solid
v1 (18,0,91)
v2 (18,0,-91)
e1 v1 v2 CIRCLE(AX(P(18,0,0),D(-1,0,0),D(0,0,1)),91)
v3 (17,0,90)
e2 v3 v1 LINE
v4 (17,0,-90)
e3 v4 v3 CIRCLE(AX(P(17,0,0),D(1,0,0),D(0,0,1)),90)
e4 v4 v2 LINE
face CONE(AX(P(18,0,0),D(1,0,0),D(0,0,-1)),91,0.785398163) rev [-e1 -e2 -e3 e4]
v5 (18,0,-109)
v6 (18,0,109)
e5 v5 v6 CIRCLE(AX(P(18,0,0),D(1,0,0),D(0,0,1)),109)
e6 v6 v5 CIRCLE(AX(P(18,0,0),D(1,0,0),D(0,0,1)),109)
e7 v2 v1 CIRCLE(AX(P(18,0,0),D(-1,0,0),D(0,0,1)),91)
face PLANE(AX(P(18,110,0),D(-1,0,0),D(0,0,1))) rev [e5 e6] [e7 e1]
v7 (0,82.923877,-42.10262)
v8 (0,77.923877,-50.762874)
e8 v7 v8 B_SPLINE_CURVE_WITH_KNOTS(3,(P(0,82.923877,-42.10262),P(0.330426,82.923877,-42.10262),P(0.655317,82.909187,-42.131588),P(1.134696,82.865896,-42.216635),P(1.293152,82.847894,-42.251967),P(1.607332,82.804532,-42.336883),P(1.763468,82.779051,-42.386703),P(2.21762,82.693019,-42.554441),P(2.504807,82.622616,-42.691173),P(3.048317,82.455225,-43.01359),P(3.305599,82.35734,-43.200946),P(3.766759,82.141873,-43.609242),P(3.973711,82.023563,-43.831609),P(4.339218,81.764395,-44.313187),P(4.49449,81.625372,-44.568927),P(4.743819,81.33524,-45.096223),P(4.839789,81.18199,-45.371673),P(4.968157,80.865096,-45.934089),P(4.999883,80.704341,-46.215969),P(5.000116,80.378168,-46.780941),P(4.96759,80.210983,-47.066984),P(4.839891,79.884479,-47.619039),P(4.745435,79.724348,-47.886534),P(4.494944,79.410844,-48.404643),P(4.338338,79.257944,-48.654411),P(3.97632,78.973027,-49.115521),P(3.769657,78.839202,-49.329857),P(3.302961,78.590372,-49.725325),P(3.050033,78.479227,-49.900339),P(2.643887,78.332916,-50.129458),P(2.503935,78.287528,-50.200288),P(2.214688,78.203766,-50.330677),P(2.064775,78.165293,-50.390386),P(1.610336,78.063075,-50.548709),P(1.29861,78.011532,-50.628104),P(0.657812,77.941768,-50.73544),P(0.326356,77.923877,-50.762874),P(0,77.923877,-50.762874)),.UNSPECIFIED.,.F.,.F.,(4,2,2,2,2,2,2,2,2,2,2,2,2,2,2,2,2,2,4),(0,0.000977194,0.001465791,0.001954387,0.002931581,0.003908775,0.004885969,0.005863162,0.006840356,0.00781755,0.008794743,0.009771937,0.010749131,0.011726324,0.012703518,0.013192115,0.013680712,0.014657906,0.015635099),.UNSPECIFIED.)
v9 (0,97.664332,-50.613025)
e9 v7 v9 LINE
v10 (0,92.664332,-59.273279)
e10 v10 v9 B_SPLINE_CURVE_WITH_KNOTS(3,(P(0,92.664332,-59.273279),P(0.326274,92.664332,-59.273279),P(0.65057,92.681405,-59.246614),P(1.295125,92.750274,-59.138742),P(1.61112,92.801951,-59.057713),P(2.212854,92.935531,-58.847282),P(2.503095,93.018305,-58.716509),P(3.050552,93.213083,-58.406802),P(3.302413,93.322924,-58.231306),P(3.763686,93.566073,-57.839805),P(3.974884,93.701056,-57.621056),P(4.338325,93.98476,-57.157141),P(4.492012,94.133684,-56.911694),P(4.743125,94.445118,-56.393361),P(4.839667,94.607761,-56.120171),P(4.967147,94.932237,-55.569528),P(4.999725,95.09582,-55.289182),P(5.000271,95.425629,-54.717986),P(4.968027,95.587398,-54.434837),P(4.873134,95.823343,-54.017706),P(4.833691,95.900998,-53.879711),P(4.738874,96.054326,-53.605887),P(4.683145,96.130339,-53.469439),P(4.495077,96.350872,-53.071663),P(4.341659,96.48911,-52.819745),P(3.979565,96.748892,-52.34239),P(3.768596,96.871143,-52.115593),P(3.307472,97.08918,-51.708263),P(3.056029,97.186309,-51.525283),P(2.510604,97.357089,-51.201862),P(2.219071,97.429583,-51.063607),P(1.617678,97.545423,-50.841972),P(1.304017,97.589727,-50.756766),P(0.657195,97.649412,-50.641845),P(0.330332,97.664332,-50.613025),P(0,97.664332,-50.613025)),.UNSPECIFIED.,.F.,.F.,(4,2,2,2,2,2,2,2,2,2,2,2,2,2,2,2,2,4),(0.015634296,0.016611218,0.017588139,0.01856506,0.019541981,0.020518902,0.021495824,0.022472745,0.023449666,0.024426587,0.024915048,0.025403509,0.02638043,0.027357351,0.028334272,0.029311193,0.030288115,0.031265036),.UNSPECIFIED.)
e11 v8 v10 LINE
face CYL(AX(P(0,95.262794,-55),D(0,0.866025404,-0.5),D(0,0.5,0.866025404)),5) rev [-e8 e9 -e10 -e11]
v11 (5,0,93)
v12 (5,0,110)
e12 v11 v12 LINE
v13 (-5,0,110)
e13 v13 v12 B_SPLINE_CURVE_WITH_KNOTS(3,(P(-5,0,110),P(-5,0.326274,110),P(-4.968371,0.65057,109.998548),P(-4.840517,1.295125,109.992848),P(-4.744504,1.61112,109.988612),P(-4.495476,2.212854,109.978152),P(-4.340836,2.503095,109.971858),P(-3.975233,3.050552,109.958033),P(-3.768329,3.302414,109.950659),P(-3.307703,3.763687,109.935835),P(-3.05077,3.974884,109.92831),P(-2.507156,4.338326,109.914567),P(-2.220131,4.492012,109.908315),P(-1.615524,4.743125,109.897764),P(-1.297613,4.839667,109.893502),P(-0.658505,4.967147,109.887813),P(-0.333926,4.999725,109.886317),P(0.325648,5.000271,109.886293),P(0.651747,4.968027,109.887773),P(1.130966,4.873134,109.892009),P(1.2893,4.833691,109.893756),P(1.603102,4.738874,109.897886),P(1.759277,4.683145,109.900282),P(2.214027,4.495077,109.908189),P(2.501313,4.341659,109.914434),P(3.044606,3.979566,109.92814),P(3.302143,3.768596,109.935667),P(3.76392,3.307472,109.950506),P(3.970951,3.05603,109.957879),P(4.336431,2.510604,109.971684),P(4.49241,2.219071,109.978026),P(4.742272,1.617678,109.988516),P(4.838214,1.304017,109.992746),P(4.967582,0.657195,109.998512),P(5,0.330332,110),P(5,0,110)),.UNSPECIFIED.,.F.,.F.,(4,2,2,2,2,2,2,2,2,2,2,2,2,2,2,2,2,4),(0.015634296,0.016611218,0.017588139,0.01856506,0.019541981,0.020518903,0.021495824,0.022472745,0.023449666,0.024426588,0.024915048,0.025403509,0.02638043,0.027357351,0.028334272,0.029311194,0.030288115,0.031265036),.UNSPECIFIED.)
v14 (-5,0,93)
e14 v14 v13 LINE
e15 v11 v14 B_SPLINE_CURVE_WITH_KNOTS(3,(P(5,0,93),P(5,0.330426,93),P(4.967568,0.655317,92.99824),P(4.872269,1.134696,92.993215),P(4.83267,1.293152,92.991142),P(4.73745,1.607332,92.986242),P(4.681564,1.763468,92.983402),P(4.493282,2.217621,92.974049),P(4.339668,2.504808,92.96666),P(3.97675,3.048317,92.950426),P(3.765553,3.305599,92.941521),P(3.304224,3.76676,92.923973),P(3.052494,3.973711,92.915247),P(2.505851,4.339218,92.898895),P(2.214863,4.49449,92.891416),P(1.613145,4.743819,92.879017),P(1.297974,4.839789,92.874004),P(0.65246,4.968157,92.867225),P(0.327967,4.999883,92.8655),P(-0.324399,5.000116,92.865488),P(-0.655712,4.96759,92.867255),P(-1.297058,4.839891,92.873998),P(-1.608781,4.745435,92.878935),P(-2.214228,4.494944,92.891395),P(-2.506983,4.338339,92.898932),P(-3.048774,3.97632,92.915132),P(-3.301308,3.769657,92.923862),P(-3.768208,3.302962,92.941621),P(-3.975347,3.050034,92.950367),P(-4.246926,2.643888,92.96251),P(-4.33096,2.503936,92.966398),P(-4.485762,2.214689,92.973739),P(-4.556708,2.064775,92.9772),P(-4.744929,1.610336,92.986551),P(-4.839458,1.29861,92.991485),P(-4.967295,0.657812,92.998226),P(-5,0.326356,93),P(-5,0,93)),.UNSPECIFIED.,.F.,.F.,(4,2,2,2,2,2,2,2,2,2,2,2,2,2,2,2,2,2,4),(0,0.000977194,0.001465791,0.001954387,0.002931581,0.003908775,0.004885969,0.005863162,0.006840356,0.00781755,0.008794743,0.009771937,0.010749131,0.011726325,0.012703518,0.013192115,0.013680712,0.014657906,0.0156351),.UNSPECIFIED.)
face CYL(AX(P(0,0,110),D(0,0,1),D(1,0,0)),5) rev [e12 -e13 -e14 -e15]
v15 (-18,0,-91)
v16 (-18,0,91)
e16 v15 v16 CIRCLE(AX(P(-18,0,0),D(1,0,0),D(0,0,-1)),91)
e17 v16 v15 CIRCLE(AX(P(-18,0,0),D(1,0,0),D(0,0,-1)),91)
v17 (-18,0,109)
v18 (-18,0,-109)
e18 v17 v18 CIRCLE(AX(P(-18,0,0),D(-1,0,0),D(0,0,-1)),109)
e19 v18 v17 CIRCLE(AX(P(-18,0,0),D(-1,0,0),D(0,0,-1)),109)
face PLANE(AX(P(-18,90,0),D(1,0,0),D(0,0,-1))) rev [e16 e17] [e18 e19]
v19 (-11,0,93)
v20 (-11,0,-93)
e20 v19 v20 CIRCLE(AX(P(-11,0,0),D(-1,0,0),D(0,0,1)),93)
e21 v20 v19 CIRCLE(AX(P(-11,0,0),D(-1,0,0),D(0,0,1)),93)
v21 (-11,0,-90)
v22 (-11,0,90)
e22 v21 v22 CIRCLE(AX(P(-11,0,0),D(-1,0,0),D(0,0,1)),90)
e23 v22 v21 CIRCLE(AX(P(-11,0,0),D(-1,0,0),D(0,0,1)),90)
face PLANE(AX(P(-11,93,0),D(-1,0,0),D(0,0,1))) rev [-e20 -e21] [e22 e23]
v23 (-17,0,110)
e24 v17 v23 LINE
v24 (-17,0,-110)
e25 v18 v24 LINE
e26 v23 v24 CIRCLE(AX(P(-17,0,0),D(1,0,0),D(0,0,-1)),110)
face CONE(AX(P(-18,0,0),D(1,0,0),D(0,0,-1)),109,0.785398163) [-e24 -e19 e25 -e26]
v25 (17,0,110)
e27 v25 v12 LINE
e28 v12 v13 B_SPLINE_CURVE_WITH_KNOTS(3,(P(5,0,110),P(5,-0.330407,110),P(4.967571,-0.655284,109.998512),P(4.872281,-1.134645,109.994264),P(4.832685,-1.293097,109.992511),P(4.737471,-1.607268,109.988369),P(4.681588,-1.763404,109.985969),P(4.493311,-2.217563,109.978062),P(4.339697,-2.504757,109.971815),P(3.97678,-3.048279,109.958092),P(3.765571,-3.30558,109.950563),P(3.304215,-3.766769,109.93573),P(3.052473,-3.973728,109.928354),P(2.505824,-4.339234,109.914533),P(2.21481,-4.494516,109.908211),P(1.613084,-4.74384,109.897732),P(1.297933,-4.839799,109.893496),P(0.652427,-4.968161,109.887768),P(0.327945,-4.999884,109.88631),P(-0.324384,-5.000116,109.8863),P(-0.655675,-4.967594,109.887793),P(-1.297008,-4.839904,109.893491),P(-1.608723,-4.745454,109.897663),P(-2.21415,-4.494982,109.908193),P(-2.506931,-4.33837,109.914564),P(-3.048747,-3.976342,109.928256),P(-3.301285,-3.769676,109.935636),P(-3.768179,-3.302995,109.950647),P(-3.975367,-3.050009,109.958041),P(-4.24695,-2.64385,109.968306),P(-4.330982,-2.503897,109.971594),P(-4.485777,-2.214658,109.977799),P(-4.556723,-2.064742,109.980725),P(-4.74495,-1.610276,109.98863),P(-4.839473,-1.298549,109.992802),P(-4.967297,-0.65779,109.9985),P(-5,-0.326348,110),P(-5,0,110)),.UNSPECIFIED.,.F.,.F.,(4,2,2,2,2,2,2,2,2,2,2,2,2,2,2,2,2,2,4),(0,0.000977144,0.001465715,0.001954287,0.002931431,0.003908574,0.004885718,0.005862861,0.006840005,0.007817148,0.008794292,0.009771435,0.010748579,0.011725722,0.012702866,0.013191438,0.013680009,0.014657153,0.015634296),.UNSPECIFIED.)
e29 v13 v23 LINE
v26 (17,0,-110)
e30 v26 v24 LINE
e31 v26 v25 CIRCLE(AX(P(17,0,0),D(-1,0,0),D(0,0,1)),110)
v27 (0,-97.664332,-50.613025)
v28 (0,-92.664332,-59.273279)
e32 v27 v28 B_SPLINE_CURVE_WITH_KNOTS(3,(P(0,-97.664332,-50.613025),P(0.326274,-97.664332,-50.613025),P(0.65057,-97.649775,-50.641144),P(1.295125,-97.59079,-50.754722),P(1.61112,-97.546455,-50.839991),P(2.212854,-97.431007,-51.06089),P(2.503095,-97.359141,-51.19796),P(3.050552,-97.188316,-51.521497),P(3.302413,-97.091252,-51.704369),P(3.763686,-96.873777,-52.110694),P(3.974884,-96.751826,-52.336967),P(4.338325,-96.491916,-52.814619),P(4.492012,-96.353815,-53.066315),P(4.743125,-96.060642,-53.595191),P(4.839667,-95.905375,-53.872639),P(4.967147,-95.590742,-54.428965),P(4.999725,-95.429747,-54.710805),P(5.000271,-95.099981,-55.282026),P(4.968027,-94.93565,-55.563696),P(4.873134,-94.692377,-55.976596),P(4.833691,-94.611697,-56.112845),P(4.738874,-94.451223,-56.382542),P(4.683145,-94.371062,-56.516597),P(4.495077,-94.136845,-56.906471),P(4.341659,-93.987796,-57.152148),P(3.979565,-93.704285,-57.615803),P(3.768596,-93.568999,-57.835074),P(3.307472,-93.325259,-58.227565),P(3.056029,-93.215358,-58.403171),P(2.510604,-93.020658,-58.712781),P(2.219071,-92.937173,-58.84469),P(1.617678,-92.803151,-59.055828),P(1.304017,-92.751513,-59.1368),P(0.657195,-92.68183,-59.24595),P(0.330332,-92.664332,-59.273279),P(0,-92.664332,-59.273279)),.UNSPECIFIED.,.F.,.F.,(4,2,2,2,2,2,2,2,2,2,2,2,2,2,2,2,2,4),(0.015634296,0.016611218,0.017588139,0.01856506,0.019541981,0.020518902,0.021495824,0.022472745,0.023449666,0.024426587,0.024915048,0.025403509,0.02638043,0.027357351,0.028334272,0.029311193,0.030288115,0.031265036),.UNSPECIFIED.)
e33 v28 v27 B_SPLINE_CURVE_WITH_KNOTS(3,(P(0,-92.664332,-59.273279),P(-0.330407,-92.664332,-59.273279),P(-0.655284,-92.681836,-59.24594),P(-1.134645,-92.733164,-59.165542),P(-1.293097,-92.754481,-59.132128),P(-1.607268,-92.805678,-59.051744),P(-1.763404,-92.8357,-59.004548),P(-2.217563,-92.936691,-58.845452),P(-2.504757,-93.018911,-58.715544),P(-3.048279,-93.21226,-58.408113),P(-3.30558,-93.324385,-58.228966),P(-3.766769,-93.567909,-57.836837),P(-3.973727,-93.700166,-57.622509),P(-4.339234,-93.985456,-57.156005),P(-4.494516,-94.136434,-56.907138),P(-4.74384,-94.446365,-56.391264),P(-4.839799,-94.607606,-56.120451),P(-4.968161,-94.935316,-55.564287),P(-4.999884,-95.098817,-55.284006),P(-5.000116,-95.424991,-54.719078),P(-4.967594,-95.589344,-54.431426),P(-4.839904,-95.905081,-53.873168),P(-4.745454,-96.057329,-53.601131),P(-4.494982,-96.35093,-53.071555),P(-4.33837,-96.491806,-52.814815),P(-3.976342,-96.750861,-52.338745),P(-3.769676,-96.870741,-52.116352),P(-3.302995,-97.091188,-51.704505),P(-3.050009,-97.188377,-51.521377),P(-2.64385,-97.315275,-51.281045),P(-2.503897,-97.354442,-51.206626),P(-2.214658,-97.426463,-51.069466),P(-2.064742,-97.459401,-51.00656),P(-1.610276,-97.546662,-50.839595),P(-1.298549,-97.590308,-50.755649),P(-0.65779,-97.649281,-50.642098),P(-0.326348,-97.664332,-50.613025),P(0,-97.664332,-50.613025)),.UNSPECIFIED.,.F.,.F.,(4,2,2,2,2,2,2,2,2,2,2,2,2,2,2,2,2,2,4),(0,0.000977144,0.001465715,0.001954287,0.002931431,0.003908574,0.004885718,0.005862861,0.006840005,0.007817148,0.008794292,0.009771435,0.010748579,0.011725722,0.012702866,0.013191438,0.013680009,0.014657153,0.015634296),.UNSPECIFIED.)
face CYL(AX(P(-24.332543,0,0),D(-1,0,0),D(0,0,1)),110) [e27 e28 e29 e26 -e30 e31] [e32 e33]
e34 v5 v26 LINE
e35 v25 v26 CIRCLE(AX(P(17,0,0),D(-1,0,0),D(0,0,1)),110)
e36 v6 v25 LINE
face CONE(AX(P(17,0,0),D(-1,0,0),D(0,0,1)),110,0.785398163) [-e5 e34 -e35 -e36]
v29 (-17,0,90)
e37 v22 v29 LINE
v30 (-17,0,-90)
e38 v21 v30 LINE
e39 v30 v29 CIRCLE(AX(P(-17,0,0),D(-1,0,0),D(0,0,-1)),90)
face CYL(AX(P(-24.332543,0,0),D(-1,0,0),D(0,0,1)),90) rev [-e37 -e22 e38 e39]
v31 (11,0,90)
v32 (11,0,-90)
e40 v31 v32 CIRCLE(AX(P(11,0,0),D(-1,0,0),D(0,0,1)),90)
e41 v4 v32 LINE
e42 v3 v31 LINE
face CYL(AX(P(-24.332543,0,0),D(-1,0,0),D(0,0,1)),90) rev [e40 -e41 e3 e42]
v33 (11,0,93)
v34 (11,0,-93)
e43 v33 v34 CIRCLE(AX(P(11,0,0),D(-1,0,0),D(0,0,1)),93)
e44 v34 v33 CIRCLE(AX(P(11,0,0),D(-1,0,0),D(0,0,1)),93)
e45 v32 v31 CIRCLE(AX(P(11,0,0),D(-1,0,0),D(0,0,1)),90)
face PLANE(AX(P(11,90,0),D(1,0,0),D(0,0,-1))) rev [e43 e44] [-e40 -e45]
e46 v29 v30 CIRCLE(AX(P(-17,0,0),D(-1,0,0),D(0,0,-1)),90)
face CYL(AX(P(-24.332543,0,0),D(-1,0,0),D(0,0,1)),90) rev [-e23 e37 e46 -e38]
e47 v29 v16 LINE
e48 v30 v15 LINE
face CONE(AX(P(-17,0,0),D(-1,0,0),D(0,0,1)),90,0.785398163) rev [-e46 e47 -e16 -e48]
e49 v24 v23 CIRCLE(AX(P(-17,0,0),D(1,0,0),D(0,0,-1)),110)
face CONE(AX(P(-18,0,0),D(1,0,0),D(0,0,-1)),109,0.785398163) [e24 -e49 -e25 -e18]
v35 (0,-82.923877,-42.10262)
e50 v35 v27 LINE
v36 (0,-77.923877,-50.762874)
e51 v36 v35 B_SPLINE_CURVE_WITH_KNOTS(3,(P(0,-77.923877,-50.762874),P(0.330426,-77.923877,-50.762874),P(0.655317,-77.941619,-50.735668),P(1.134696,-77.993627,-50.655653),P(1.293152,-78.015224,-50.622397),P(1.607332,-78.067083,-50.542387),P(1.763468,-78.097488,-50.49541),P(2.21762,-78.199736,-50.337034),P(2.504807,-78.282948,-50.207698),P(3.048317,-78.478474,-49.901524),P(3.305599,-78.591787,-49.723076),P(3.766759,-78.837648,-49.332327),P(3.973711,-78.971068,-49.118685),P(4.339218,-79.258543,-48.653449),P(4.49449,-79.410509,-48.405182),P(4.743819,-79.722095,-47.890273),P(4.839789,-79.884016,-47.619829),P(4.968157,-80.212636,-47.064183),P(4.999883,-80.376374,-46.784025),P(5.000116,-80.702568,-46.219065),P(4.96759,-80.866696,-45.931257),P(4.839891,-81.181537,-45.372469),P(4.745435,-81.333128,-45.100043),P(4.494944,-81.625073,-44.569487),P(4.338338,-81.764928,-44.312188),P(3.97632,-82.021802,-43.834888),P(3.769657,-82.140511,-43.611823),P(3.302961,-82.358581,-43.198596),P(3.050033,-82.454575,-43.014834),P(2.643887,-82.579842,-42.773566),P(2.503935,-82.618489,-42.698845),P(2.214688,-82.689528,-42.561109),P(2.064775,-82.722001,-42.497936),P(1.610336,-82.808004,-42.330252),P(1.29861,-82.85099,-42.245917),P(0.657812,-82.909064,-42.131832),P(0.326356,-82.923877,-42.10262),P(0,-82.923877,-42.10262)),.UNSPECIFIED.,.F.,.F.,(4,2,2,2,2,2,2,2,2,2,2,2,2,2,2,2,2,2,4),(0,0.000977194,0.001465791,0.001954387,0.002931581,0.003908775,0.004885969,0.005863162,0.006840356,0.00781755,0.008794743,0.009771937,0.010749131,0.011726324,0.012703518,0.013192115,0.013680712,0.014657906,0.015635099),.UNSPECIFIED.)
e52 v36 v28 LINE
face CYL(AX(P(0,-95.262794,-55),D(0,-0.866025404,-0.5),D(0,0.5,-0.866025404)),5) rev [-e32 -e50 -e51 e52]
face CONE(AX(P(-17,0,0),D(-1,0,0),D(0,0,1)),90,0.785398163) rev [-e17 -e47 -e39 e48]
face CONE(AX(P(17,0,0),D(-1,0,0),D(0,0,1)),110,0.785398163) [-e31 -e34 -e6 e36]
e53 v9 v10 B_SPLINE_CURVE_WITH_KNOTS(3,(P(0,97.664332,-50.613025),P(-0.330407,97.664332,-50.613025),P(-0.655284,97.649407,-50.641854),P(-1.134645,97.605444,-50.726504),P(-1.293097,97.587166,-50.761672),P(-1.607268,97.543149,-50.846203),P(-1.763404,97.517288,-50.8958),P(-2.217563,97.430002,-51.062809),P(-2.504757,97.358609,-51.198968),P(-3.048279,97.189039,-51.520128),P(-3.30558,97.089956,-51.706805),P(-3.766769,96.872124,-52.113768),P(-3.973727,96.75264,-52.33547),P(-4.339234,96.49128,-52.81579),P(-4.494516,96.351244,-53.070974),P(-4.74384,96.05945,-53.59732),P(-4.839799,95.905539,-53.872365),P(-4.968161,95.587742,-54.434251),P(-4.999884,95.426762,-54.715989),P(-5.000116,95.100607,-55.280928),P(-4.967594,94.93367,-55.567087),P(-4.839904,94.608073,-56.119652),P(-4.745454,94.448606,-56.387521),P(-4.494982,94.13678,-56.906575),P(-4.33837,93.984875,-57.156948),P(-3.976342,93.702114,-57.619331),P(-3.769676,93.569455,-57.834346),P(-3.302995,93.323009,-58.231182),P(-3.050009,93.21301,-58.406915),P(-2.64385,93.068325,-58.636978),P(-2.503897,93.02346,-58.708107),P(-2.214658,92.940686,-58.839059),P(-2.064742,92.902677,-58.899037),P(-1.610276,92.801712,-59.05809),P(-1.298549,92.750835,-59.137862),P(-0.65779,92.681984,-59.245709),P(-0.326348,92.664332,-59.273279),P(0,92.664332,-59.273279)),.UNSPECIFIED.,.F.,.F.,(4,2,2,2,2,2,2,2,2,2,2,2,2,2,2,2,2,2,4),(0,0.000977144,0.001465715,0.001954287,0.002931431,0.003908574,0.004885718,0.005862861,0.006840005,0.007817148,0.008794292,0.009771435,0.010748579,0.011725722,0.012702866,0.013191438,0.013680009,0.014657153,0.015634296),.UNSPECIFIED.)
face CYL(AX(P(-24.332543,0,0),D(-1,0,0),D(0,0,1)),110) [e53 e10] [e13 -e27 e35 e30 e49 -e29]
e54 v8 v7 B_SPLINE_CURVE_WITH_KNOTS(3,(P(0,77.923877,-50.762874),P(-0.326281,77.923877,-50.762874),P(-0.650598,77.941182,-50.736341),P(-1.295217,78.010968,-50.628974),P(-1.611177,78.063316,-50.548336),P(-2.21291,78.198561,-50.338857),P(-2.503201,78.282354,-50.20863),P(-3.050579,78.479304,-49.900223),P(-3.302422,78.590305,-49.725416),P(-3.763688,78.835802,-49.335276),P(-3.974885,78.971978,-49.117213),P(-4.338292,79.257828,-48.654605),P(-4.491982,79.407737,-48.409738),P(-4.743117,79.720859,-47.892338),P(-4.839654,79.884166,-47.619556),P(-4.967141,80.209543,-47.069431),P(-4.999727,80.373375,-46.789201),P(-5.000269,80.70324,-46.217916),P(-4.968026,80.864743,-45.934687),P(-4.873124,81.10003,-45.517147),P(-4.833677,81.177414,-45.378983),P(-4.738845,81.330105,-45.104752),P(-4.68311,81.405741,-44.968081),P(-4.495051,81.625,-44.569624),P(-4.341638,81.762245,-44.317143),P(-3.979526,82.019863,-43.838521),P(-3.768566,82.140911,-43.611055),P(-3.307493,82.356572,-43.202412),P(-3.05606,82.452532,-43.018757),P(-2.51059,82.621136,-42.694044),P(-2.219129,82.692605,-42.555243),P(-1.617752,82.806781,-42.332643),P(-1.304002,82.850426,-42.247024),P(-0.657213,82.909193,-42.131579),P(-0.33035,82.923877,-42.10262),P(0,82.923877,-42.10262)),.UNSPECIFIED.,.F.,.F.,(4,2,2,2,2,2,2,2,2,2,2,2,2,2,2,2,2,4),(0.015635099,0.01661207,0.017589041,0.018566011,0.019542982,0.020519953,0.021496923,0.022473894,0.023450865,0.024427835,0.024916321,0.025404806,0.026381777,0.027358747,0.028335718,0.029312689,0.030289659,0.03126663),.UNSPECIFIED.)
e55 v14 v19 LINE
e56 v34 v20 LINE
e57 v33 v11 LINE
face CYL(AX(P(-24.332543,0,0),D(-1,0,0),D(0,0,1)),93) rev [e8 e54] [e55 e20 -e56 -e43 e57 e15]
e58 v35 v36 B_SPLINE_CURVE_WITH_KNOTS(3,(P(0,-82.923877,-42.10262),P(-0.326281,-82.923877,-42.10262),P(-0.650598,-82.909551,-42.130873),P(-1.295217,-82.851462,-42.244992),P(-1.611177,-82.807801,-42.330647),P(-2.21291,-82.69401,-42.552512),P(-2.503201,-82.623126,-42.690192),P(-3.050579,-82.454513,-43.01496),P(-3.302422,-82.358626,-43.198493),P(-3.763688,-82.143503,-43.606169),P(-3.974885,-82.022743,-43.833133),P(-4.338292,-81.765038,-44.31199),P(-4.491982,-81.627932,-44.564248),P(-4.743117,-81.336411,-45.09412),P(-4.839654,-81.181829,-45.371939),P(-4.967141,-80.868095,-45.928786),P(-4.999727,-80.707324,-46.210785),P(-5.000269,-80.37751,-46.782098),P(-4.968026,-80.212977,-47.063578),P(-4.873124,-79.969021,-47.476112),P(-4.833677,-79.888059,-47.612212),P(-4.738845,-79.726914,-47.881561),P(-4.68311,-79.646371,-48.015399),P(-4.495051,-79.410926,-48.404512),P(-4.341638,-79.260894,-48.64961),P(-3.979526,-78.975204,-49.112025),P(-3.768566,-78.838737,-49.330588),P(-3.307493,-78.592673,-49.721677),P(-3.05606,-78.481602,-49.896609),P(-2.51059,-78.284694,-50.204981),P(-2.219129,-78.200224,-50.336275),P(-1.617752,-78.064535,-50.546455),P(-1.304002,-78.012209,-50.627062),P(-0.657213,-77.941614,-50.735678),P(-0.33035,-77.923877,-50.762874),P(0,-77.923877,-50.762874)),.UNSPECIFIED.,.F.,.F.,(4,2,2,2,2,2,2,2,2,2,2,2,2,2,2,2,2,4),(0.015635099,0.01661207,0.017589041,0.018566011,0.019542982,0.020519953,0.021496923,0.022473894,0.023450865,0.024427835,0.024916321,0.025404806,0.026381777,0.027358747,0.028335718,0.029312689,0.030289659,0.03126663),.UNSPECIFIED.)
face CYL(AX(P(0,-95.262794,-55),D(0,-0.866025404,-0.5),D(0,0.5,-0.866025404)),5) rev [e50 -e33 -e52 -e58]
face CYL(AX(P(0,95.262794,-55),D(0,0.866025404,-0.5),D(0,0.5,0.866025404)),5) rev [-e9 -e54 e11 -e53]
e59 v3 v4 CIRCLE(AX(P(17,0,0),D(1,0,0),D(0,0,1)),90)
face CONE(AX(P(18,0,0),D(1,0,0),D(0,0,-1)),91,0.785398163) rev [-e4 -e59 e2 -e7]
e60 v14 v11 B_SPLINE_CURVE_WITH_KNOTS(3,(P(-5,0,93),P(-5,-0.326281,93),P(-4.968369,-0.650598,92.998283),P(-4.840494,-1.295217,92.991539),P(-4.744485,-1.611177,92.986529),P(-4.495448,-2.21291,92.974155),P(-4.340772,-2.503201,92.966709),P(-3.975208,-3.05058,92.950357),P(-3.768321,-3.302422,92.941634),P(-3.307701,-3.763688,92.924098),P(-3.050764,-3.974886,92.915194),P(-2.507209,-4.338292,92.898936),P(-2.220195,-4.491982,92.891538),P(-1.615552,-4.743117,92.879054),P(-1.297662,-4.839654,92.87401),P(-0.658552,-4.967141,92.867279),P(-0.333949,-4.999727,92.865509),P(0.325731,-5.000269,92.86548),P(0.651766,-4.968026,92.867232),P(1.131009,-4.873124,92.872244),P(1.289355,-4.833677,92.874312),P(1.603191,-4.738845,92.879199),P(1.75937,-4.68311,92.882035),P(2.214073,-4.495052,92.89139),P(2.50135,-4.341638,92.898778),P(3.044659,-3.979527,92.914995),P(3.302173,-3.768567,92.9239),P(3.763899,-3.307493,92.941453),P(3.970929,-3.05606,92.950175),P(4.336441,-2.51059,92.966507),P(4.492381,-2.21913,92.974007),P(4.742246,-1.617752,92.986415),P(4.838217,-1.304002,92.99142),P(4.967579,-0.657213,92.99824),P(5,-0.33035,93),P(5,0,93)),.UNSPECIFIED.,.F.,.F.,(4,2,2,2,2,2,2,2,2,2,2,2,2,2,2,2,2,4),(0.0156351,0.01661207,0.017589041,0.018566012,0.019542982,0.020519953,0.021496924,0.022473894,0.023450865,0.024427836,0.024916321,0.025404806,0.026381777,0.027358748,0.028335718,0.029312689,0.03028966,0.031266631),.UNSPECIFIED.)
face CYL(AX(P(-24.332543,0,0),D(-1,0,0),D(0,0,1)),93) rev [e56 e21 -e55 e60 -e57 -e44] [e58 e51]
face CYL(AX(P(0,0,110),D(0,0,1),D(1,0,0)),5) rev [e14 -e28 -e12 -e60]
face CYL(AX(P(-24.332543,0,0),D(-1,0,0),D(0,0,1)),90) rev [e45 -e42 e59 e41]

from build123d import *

# Parameters (mm, degrees)
CHAMFER1_SIZE     = 1
HOLE1_D           = 10
HOLE1_DEPTH       = 18
CIRPATTERN1_COUNT = 3


with BuildPart() as part:
    # Sketch2 → Revolve1 (revolve)
    with BuildSketch(Plane.XY, mode=Mode.PRIVATE) as revolve1_sk:
        Polygon((-18, 90), (-18, 110), (18, 110), (18, 90), (11, 90), (11, 93), (-11, 93), (-11, 90), align=None)
    revolve(revolve1_sk.sketch.rotate(Axis((-24.332542805, 0, 0), (1, 0, 0)), 90), axis=Axis((-24.332542805, 0, 0), (1, 0, 0)))

    # Chamfer1
    chamfer1_edges = [part.edges().sort_by_distance(p)[0] for p in [
        (-18, 0, -110),
        (-18, 0, -90),
        (18, 0, -90),
        (18, 0, -110),
    ]]
    chamfer(chamfer1_edges, length=CHAMFER1_SIZE)

    # Hole1
    with Locations(Plane.XY.offset(110)):
        with Locations((0, 0)):
            hole1 = Hole(HOLE1_D / 2, depth=HOLE1_DEPTH)

    # CirPattern1: Hole1 ×3 about axis
    cirpattern1_axis = Axis((17, 0, 0), (-1, 0, 0))
    for i in range(1, CIRPATTERN1_COUNT):
        add(hole1.rotate(cirpattern1_axis, i * 360 / CIRPATTERN1_COUNT), mode=Mode.SUBTRACT)


solid = part.part
